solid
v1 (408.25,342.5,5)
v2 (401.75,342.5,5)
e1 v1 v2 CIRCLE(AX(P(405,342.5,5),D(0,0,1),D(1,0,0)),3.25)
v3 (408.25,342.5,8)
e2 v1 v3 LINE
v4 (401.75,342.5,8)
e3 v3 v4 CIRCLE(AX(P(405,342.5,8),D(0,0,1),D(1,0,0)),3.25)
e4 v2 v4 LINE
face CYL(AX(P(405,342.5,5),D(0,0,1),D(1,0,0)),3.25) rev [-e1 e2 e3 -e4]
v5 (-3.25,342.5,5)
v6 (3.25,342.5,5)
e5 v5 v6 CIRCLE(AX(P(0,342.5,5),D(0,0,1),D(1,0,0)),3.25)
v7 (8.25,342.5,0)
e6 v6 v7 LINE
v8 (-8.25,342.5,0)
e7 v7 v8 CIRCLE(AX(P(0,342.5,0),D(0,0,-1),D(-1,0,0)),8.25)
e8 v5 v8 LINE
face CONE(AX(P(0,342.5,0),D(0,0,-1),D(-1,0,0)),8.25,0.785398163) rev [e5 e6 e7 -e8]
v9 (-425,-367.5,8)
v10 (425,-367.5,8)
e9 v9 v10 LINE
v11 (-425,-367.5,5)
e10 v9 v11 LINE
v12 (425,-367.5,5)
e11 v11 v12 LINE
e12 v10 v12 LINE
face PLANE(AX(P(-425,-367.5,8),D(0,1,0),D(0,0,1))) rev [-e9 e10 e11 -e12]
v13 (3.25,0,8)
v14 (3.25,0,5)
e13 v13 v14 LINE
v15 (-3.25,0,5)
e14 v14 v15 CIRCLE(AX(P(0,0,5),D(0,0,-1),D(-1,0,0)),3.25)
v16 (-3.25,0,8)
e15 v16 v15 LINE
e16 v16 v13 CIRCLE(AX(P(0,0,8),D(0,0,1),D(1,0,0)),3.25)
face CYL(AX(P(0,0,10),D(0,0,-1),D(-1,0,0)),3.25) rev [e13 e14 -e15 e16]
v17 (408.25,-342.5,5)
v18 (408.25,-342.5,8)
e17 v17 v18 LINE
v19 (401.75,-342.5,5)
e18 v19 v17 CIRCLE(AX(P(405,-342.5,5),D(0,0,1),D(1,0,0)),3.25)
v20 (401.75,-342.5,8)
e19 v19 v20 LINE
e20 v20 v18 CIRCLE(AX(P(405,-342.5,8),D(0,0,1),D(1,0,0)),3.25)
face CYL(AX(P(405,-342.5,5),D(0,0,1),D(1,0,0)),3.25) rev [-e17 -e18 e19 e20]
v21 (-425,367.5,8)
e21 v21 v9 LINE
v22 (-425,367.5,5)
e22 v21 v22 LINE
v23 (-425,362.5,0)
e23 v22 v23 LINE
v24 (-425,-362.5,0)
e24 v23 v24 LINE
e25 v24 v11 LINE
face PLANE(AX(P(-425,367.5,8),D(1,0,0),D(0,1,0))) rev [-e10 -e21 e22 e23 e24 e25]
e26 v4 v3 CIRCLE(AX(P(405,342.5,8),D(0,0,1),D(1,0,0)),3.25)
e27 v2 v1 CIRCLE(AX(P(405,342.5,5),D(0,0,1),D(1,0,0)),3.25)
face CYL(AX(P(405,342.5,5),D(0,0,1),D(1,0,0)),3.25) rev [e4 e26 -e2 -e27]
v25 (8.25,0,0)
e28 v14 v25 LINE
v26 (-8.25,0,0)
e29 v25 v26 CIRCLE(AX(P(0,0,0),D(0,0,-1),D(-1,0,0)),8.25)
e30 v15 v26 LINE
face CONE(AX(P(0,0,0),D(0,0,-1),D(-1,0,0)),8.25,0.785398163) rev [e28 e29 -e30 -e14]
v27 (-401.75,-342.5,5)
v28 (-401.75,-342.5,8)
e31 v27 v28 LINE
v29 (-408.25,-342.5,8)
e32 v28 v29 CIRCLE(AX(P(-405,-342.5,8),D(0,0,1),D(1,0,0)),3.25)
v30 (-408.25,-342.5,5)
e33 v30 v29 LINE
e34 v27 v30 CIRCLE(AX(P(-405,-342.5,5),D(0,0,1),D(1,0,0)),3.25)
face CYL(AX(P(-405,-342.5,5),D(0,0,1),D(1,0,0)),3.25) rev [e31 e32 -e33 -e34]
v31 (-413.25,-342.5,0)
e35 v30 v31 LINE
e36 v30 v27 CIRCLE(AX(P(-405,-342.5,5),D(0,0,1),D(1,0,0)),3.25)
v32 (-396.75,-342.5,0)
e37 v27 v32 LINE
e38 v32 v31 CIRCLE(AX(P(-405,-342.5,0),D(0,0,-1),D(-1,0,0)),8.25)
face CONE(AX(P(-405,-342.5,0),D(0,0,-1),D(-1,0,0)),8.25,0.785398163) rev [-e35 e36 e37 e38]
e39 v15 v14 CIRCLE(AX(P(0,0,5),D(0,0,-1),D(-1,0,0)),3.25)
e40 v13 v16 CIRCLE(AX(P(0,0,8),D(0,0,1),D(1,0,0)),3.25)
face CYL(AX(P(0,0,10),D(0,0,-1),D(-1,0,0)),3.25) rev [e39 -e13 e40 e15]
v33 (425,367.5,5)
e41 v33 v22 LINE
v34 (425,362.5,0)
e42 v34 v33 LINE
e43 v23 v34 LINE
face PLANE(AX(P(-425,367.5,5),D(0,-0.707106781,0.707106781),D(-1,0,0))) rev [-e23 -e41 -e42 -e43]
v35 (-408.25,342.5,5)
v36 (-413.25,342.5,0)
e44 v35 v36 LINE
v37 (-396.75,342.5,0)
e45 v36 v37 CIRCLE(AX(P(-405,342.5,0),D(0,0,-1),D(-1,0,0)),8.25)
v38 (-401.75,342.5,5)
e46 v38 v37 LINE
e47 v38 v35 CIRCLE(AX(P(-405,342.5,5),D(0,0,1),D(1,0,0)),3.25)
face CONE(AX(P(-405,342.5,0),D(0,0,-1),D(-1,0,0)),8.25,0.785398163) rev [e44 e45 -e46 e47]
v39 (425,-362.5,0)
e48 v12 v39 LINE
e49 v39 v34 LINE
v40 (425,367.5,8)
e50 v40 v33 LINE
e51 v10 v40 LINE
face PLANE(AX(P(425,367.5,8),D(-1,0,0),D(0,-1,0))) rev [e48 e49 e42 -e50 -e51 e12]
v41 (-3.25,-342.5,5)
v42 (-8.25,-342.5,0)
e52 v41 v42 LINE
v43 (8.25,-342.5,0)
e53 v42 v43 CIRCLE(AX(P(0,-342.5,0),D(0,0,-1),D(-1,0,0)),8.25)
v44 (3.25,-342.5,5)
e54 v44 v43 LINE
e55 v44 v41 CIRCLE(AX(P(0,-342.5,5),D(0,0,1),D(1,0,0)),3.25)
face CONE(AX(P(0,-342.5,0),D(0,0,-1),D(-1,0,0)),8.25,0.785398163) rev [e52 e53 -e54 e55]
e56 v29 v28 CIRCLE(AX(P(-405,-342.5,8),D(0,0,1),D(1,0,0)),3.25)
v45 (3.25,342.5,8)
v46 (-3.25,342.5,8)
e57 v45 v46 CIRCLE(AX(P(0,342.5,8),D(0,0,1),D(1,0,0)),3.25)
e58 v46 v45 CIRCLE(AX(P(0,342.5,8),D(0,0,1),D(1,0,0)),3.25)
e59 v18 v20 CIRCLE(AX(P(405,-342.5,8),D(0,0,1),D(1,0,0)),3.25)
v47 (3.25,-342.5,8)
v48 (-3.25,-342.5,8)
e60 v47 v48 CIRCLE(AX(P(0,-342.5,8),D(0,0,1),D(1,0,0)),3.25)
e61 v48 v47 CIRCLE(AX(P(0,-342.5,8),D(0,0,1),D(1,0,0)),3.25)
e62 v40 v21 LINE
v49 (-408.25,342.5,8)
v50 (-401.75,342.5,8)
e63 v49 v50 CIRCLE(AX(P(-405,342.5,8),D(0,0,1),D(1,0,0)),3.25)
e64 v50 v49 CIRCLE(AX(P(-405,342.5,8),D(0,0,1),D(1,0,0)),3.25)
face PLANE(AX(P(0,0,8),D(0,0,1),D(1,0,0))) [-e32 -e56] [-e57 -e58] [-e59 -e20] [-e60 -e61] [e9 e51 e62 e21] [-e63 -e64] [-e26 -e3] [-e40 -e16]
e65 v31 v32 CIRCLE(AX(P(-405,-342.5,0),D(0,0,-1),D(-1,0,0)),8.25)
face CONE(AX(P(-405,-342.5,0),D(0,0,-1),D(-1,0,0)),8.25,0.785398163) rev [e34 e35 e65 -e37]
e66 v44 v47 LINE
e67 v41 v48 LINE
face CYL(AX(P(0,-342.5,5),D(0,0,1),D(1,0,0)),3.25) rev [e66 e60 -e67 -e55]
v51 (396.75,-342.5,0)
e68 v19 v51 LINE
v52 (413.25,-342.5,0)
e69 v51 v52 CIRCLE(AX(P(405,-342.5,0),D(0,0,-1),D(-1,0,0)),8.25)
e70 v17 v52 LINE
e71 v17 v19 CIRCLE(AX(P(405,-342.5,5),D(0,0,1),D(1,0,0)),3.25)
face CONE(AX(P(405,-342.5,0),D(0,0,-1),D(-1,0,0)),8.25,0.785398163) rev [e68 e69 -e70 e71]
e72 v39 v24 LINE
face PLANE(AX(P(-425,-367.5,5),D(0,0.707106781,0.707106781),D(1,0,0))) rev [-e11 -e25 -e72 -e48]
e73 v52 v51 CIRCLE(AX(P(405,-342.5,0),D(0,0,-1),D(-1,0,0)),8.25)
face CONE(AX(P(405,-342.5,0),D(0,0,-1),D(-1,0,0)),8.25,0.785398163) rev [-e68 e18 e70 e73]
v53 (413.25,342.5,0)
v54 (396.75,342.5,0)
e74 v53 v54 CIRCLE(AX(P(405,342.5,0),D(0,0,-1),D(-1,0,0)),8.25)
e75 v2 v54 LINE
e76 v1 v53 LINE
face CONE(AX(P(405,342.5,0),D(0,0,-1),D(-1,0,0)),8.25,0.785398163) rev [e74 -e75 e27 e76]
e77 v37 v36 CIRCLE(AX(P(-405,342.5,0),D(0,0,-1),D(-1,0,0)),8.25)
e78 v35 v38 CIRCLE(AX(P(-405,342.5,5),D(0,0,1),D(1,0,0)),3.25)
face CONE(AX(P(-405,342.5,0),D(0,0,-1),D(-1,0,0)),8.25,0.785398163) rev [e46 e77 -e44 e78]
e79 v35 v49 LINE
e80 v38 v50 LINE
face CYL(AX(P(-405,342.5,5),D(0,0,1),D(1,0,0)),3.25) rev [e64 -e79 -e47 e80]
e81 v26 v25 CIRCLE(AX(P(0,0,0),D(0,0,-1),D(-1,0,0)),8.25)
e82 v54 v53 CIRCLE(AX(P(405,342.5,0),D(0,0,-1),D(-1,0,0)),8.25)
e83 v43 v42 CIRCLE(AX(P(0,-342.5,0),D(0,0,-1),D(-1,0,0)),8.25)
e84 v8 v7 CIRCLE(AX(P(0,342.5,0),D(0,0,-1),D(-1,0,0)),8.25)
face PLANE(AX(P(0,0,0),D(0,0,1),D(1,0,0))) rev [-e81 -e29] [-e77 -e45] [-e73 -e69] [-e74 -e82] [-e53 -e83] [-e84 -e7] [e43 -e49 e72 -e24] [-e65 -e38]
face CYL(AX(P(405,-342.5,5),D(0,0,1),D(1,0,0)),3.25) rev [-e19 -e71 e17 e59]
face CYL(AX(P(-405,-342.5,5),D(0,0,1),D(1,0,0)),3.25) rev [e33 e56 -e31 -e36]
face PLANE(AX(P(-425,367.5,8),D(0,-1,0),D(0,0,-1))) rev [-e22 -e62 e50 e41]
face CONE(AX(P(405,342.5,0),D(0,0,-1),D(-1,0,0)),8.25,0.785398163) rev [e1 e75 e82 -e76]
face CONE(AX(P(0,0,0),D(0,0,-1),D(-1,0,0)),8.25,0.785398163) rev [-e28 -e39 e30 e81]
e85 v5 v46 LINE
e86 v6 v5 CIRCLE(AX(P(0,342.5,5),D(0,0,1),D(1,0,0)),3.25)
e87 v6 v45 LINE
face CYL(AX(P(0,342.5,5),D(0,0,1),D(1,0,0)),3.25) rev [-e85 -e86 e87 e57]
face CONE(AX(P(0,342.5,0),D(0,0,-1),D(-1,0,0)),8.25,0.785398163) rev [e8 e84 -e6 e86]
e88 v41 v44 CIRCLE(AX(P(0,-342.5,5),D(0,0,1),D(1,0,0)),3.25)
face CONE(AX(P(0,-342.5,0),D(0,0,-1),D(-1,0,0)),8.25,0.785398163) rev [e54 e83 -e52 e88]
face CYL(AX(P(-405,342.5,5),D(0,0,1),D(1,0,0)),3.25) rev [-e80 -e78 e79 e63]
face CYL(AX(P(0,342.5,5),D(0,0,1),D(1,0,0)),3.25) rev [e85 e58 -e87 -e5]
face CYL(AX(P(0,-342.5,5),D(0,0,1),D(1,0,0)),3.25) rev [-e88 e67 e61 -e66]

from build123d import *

# Parameters (mm, degrees)
SKETCH_1_W                    = 850
SKETCH_1_H                    = 735
EXTRUDE_1_DEPTH               = 8
CHAMFER_1_SIZE                = 5
SKETCH_2_R                    = 8.25
CUT_EXTRUDE_1_DEPTH           = 5
CUT_EXTRUDE_1_DRAFT           = -45
CUT_EXTRUDE_1_PROFILE_2_DEPTH = 5
CUT_EXTRUDE_1_PROFILE_2_DRAFT = -45
CUT_EXTRUDE_1_PROFILE_3_DEPTH = 5
CUT_EXTRUDE_1_PROFILE_3_DRAFT = -45
CUT_EXTRUDE_1_PROFILE_4_DEPTH = 5
CUT_EXTRUDE_1_PROFILE_4_DRAFT = -45
CUT_EXTRUDE_1_PROFILE_5_DEPTH = 5
CUT_EXTRUDE_1_PROFILE_5_DRAFT = -45
CUT_EXTRUDE_1_PROFILE_6_DEPTH = 5
CUT_EXTRUDE_1_PROFILE_6_DRAFT = -45
SKETCH_3_R                    = 3.25
CUT_EXTRUDE_2_DEPTH           = 3
SKETCH_4_R                    = 8.25
CUT_EXTRUDE_3_DEPTH           = 5
CUT_EXTRUDE_3_DRAFT           = -45
SKETCH_5_R                    = 3.25
CUT_EXTRUDE_4_DEPTH           = 5


with BuildPart() as part:
    # 草图1 → 凸台-拉伸1 (new body)
    with BuildSketch(Plane.XY):
        Rectangle(SKETCH_1_W, SKETCH_1_H)
    extrude(amount=EXTRUDE_1_DEPTH)

    # 倒角1
    chamfer_1_edges = [part.edges().sort_by_distance(p)[0] for p in [
        (0, -367.5, 0),
        (0, 367.5, 0),
    ]]
    chamfer(chamfer_1_edges, length=CHAMFER_1_SIZE)


with BuildPart() as cut_extrude_1_tool:
    # 草图2 → 切除-拉伸1 (with draft: the straight prism first)
    with BuildSketch(Plane(origin=(0, 0, 0), x_dir=(-1, 0, 0), z_dir=(0, 0, -1))):
        with Locations((-405, 342.5)):
            Circle(SKETCH_2_R)
    extrude(amount=-CUT_EXTRUDE_1_DEPTH)
    # 切除-拉伸1: the draft: its side faces are tilted about the plane it starts from
    cut_extrude_1_sides = [cut_extrude_1_tool.faces().sort_by_distance(p)[0] for p in [
        (413.25, 342.5, 2.5),
    ]]
    draft(cut_extrude_1_sides, Plane(origin=(0, 0, 0), x_dir=(-1, 0, 0), z_dir=(0, 0, -1)), CUT_EXTRUDE_1_DRAFT)


with BuildPart() as part_1:
    add(part.part)

    # 切除-拉伸1: cut by cut_extrude_1_tool
    add(cut_extrude_1_tool.part, mode=Mode.SUBTRACT)


with BuildPart() as cut_extrude_1_profile_2_tool:
    # 草图2 → 切除-拉伸1 profile 2 (with draft: the straight prism first)
    with BuildSketch(Plane(origin=(0, 0, 0), x_dir=(-1, 0, 0), z_dir=(0, 0, -1))):
        with Locations((0, 342.5)):
            Circle(SKETCH_2_R)
    extrude(amount=-CUT_EXTRUDE_1_PROFILE_2_DEPTH)
    # 切除-拉伸1 profile 2: the draft: its side faces are tilted about the plane it starts from
    cut_extrude_1_profile_2_sides = [cut_extrude_1_profile_2_tool.faces().sort_by_distance(p)[0] for p in [
        (8.25, 342.5, 2.5),
    ]]
    draft(cut_extrude_1_profile_2_sides, Plane(origin=(0, 0, 0), x_dir=(-1, 0, 0), z_dir=(0, 0, -1)), CUT_EXTRUDE_1_PROFILE_2_DRAFT)


with BuildPart() as part_2:
    add(part_1.part)

    # 切除-拉伸1 profile 2: cut by cut_extrude_1_profile_2_tool
    add(cut_extrude_1_profile_2_tool.part, mode=Mode.SUBTRACT)


with BuildPart() as cut_extrude_1_profile_3_tool:
    # 草图2 → 切除-拉伸1 profile 3 (with draft: the straight prism first)
    with BuildSketch(Plane(origin=(0, 0, 0), x_dir=(-1, 0, 0), z_dir=(0, 0, -1))):
        with Locations((405, 342.5)):
            Circle(SKETCH_2_R)
    extrude(amount=-CUT_EXTRUDE_1_PROFILE_3_DEPTH)
    # 切除-拉伸1 profile 3: the draft: its side faces are tilted about the plane it starts from
    cut_extrude_1_profile_3_sides = [cut_extrude_1_profile_3_tool.faces().sort_by_distance(p)[0] for p in [
        (-396.75, 342.5, 2.5),
    ]]
    draft(cut_extrude_1_profile_3_sides, Plane(origin=(0, 0, 0), x_dir=(-1, 0, 0), z_dir=(0, 0, -1)), CUT_EXTRUDE_1_PROFILE_3_DRAFT)


with BuildPart() as part_3:
    add(part_2.part)

    # 切除-拉伸1 profile 3: cut by cut_extrude_1_profile_3_tool
    add(cut_extrude_1_profile_3_tool.part, mode=Mode.SUBTRACT)


with BuildPart() as cut_extrude_1_profile_4_tool:
    # 草图2 → 切除-拉伸1 profile 4 (with draft: the straight prism first)
    with BuildSketch(Plane(origin=(0, 0, 0), x_dir=(-1, 0, 0), z_dir=(0, 0, -1))):
        with Locations((-405, -342.5)):
            Circle(SKETCH_2_R)
    extrude(amount=-CUT_EXTRUDE_1_PROFILE_4_DEPTH)
    # 切除-拉伸1 profile 4: the draft: its side faces are tilted about the plane it starts from
    cut_extrude_1_profile_4_sides = [cut_extrude_1_profile_4_tool.faces().sort_by_distance(p)[0] for p in [
        (413.25, -342.5, 2.5),
    ]]
    draft(cut_extrude_1_profile_4_sides, Plane(origin=(0, 0, 0), x_dir=(-1, 0, 0), z_dir=(0, 0, -1)), CUT_EXTRUDE_1_PROFILE_4_DRAFT)


with BuildPart() as part_4:
    add(part_3.part)

    # 切除-拉伸1 profile 4: cut by cut_extrude_1_profile_4_tool
    add(cut_extrude_1_profile_4_tool.part, mode=Mode.SUBTRACT)


with BuildPart() as cut_extrude_1_profile_5_tool:
    # 草图2 → 切除-拉伸1 profile 5 (with draft: the straight prism first)
    with BuildSketch(Plane(origin=(0, 0, 0), x_dir=(-1, 0, 0), z_dir=(0, 0, -1))):
        with Locations((0, -342.5)):
            Circle(SKETCH_2_R)
    extrude(amount=-CUT_EXTRUDE_1_PROFILE_5_DEPTH)
    # 切除-拉伸1 profile 5: the draft: its side faces are tilted about the plane it starts from
    cut_extrude_1_profile_5_sides = [cut_extrude_1_profile_5_tool.faces().sort_by_distance(p)[0] for p in [
        (8.25, -342.5, 2.5),
    ]]
    draft(cut_extrude_1_profile_5_sides, Plane(origin=(0, 0, 0), x_dir=(-1, 0, 0), z_dir=(0, 0, -1)), CUT_EXTRUDE_1_PROFILE_5_DRAFT)


with BuildPart() as part_5:
    add(part_4.part)

    # 切除-拉伸1 profile 5: cut by cut_extrude_1_profile_5_tool
    add(cut_extrude_1_profile_5_tool.part, mode=Mode.SUBTRACT)


with BuildPart() as cut_extrude_1_profile_6_tool:
    # 草图2 → 切除-拉伸1 profile 6 (with draft: the straight prism first)
    with BuildSketch(Plane(origin=(0, 0, 0), x_dir=(-1, 0, 0), z_dir=(0, 0, -1))):
        with Locations((405, -342.5)):
            Circle(SKETCH_2_R)
    extrude(amount=-CUT_EXTRUDE_1_PROFILE_6_DEPTH)
    # 切除-拉伸1 profile 6: the draft: its side faces are tilted about the plane it starts from
    cut_extrude_1_profile_6_sides = [cut_extrude_1_profile_6_tool.faces().sort_by_distance(p)[0] for p in [
        (-396.75, -342.5, 2.5),
    ]]
    draft(cut_extrude_1_profile_6_sides, Plane(origin=(0, 0, 0), x_dir=(-1, 0, 0), z_dir=(0, 0, -1)), CUT_EXTRUDE_1_PROFILE_6_DRAFT)


with BuildPart() as part_6:
    add(part_5.part)

    # 切除-拉伸1 profile 6: cut by cut_extrude_1_profile_6_tool
    add(cut_extrude_1_profile_6_tool.part, mode=Mode.SUBTRACT)

    # 草图3 → 切除-拉伸2 (cut)
    with BuildSketch(Plane.XY.offset(8)):
        with Locations((-405, 342.5)):
            Circle(SKETCH_3_R)
        with Locations((0, 342.5)):
            Circle(SKETCH_3_R)
        with Locations((405, 342.5)):
            Circle(SKETCH_3_R)
        with Locations((-405, -342.5)):
            Circle(SKETCH_3_R)
        with Locations((0, -342.5)):
            Circle(SKETCH_3_R)
        with Locations((405, -342.5)):
            Circle(SKETCH_3_R)
    extrude(amount=-CUT_EXTRUDE_2_DEPTH, mode=Mode.SUBTRACT)


with BuildPart() as cut_extrude_3_tool:
    # 草图4 → 切除-拉伸3 (with draft: the straight prism first)
    with BuildSketch(Plane(origin=(0, 0, 0), x_dir=(-1, 0, 0), z_dir=(0, 0, -1))):
        Circle(SKETCH_4_R)
    extrude(amount=-CUT_EXTRUDE_3_DEPTH)
    # 切除-拉伸3: the draft: its side faces are tilted about the plane it starts from
    cut_extrude_3_sides = [cut_extrude_3_tool.faces().sort_by_distance(p)[0] for p in [
        (8.25, 0, 2.5),
    ]]
    draft(cut_extrude_3_sides, Plane(origin=(0, 0, 0), x_dir=(-1, 0, 0), z_dir=(0, 0, -1)), CUT_EXTRUDE_3_DRAFT)


with BuildPart() as part_7:
    add(part_6.part)

    # 切除-拉伸3: cut by cut_extrude_3_tool
    add(cut_extrude_3_tool.part, mode=Mode.SUBTRACT)

    # 草图5 → 切除-拉伸4 (cut)
    with BuildSketch(Plane(origin=(0, 0, 5), x_dir=(-1, 0, 0), z_dir=(0, 0, -1))):
        Circle(SKETCH_5_R)
    extrude(amount=-CUT_EXTRUDE_4_DEPTH, mode=Mode.SUBTRACT)


solid = part_7.part
